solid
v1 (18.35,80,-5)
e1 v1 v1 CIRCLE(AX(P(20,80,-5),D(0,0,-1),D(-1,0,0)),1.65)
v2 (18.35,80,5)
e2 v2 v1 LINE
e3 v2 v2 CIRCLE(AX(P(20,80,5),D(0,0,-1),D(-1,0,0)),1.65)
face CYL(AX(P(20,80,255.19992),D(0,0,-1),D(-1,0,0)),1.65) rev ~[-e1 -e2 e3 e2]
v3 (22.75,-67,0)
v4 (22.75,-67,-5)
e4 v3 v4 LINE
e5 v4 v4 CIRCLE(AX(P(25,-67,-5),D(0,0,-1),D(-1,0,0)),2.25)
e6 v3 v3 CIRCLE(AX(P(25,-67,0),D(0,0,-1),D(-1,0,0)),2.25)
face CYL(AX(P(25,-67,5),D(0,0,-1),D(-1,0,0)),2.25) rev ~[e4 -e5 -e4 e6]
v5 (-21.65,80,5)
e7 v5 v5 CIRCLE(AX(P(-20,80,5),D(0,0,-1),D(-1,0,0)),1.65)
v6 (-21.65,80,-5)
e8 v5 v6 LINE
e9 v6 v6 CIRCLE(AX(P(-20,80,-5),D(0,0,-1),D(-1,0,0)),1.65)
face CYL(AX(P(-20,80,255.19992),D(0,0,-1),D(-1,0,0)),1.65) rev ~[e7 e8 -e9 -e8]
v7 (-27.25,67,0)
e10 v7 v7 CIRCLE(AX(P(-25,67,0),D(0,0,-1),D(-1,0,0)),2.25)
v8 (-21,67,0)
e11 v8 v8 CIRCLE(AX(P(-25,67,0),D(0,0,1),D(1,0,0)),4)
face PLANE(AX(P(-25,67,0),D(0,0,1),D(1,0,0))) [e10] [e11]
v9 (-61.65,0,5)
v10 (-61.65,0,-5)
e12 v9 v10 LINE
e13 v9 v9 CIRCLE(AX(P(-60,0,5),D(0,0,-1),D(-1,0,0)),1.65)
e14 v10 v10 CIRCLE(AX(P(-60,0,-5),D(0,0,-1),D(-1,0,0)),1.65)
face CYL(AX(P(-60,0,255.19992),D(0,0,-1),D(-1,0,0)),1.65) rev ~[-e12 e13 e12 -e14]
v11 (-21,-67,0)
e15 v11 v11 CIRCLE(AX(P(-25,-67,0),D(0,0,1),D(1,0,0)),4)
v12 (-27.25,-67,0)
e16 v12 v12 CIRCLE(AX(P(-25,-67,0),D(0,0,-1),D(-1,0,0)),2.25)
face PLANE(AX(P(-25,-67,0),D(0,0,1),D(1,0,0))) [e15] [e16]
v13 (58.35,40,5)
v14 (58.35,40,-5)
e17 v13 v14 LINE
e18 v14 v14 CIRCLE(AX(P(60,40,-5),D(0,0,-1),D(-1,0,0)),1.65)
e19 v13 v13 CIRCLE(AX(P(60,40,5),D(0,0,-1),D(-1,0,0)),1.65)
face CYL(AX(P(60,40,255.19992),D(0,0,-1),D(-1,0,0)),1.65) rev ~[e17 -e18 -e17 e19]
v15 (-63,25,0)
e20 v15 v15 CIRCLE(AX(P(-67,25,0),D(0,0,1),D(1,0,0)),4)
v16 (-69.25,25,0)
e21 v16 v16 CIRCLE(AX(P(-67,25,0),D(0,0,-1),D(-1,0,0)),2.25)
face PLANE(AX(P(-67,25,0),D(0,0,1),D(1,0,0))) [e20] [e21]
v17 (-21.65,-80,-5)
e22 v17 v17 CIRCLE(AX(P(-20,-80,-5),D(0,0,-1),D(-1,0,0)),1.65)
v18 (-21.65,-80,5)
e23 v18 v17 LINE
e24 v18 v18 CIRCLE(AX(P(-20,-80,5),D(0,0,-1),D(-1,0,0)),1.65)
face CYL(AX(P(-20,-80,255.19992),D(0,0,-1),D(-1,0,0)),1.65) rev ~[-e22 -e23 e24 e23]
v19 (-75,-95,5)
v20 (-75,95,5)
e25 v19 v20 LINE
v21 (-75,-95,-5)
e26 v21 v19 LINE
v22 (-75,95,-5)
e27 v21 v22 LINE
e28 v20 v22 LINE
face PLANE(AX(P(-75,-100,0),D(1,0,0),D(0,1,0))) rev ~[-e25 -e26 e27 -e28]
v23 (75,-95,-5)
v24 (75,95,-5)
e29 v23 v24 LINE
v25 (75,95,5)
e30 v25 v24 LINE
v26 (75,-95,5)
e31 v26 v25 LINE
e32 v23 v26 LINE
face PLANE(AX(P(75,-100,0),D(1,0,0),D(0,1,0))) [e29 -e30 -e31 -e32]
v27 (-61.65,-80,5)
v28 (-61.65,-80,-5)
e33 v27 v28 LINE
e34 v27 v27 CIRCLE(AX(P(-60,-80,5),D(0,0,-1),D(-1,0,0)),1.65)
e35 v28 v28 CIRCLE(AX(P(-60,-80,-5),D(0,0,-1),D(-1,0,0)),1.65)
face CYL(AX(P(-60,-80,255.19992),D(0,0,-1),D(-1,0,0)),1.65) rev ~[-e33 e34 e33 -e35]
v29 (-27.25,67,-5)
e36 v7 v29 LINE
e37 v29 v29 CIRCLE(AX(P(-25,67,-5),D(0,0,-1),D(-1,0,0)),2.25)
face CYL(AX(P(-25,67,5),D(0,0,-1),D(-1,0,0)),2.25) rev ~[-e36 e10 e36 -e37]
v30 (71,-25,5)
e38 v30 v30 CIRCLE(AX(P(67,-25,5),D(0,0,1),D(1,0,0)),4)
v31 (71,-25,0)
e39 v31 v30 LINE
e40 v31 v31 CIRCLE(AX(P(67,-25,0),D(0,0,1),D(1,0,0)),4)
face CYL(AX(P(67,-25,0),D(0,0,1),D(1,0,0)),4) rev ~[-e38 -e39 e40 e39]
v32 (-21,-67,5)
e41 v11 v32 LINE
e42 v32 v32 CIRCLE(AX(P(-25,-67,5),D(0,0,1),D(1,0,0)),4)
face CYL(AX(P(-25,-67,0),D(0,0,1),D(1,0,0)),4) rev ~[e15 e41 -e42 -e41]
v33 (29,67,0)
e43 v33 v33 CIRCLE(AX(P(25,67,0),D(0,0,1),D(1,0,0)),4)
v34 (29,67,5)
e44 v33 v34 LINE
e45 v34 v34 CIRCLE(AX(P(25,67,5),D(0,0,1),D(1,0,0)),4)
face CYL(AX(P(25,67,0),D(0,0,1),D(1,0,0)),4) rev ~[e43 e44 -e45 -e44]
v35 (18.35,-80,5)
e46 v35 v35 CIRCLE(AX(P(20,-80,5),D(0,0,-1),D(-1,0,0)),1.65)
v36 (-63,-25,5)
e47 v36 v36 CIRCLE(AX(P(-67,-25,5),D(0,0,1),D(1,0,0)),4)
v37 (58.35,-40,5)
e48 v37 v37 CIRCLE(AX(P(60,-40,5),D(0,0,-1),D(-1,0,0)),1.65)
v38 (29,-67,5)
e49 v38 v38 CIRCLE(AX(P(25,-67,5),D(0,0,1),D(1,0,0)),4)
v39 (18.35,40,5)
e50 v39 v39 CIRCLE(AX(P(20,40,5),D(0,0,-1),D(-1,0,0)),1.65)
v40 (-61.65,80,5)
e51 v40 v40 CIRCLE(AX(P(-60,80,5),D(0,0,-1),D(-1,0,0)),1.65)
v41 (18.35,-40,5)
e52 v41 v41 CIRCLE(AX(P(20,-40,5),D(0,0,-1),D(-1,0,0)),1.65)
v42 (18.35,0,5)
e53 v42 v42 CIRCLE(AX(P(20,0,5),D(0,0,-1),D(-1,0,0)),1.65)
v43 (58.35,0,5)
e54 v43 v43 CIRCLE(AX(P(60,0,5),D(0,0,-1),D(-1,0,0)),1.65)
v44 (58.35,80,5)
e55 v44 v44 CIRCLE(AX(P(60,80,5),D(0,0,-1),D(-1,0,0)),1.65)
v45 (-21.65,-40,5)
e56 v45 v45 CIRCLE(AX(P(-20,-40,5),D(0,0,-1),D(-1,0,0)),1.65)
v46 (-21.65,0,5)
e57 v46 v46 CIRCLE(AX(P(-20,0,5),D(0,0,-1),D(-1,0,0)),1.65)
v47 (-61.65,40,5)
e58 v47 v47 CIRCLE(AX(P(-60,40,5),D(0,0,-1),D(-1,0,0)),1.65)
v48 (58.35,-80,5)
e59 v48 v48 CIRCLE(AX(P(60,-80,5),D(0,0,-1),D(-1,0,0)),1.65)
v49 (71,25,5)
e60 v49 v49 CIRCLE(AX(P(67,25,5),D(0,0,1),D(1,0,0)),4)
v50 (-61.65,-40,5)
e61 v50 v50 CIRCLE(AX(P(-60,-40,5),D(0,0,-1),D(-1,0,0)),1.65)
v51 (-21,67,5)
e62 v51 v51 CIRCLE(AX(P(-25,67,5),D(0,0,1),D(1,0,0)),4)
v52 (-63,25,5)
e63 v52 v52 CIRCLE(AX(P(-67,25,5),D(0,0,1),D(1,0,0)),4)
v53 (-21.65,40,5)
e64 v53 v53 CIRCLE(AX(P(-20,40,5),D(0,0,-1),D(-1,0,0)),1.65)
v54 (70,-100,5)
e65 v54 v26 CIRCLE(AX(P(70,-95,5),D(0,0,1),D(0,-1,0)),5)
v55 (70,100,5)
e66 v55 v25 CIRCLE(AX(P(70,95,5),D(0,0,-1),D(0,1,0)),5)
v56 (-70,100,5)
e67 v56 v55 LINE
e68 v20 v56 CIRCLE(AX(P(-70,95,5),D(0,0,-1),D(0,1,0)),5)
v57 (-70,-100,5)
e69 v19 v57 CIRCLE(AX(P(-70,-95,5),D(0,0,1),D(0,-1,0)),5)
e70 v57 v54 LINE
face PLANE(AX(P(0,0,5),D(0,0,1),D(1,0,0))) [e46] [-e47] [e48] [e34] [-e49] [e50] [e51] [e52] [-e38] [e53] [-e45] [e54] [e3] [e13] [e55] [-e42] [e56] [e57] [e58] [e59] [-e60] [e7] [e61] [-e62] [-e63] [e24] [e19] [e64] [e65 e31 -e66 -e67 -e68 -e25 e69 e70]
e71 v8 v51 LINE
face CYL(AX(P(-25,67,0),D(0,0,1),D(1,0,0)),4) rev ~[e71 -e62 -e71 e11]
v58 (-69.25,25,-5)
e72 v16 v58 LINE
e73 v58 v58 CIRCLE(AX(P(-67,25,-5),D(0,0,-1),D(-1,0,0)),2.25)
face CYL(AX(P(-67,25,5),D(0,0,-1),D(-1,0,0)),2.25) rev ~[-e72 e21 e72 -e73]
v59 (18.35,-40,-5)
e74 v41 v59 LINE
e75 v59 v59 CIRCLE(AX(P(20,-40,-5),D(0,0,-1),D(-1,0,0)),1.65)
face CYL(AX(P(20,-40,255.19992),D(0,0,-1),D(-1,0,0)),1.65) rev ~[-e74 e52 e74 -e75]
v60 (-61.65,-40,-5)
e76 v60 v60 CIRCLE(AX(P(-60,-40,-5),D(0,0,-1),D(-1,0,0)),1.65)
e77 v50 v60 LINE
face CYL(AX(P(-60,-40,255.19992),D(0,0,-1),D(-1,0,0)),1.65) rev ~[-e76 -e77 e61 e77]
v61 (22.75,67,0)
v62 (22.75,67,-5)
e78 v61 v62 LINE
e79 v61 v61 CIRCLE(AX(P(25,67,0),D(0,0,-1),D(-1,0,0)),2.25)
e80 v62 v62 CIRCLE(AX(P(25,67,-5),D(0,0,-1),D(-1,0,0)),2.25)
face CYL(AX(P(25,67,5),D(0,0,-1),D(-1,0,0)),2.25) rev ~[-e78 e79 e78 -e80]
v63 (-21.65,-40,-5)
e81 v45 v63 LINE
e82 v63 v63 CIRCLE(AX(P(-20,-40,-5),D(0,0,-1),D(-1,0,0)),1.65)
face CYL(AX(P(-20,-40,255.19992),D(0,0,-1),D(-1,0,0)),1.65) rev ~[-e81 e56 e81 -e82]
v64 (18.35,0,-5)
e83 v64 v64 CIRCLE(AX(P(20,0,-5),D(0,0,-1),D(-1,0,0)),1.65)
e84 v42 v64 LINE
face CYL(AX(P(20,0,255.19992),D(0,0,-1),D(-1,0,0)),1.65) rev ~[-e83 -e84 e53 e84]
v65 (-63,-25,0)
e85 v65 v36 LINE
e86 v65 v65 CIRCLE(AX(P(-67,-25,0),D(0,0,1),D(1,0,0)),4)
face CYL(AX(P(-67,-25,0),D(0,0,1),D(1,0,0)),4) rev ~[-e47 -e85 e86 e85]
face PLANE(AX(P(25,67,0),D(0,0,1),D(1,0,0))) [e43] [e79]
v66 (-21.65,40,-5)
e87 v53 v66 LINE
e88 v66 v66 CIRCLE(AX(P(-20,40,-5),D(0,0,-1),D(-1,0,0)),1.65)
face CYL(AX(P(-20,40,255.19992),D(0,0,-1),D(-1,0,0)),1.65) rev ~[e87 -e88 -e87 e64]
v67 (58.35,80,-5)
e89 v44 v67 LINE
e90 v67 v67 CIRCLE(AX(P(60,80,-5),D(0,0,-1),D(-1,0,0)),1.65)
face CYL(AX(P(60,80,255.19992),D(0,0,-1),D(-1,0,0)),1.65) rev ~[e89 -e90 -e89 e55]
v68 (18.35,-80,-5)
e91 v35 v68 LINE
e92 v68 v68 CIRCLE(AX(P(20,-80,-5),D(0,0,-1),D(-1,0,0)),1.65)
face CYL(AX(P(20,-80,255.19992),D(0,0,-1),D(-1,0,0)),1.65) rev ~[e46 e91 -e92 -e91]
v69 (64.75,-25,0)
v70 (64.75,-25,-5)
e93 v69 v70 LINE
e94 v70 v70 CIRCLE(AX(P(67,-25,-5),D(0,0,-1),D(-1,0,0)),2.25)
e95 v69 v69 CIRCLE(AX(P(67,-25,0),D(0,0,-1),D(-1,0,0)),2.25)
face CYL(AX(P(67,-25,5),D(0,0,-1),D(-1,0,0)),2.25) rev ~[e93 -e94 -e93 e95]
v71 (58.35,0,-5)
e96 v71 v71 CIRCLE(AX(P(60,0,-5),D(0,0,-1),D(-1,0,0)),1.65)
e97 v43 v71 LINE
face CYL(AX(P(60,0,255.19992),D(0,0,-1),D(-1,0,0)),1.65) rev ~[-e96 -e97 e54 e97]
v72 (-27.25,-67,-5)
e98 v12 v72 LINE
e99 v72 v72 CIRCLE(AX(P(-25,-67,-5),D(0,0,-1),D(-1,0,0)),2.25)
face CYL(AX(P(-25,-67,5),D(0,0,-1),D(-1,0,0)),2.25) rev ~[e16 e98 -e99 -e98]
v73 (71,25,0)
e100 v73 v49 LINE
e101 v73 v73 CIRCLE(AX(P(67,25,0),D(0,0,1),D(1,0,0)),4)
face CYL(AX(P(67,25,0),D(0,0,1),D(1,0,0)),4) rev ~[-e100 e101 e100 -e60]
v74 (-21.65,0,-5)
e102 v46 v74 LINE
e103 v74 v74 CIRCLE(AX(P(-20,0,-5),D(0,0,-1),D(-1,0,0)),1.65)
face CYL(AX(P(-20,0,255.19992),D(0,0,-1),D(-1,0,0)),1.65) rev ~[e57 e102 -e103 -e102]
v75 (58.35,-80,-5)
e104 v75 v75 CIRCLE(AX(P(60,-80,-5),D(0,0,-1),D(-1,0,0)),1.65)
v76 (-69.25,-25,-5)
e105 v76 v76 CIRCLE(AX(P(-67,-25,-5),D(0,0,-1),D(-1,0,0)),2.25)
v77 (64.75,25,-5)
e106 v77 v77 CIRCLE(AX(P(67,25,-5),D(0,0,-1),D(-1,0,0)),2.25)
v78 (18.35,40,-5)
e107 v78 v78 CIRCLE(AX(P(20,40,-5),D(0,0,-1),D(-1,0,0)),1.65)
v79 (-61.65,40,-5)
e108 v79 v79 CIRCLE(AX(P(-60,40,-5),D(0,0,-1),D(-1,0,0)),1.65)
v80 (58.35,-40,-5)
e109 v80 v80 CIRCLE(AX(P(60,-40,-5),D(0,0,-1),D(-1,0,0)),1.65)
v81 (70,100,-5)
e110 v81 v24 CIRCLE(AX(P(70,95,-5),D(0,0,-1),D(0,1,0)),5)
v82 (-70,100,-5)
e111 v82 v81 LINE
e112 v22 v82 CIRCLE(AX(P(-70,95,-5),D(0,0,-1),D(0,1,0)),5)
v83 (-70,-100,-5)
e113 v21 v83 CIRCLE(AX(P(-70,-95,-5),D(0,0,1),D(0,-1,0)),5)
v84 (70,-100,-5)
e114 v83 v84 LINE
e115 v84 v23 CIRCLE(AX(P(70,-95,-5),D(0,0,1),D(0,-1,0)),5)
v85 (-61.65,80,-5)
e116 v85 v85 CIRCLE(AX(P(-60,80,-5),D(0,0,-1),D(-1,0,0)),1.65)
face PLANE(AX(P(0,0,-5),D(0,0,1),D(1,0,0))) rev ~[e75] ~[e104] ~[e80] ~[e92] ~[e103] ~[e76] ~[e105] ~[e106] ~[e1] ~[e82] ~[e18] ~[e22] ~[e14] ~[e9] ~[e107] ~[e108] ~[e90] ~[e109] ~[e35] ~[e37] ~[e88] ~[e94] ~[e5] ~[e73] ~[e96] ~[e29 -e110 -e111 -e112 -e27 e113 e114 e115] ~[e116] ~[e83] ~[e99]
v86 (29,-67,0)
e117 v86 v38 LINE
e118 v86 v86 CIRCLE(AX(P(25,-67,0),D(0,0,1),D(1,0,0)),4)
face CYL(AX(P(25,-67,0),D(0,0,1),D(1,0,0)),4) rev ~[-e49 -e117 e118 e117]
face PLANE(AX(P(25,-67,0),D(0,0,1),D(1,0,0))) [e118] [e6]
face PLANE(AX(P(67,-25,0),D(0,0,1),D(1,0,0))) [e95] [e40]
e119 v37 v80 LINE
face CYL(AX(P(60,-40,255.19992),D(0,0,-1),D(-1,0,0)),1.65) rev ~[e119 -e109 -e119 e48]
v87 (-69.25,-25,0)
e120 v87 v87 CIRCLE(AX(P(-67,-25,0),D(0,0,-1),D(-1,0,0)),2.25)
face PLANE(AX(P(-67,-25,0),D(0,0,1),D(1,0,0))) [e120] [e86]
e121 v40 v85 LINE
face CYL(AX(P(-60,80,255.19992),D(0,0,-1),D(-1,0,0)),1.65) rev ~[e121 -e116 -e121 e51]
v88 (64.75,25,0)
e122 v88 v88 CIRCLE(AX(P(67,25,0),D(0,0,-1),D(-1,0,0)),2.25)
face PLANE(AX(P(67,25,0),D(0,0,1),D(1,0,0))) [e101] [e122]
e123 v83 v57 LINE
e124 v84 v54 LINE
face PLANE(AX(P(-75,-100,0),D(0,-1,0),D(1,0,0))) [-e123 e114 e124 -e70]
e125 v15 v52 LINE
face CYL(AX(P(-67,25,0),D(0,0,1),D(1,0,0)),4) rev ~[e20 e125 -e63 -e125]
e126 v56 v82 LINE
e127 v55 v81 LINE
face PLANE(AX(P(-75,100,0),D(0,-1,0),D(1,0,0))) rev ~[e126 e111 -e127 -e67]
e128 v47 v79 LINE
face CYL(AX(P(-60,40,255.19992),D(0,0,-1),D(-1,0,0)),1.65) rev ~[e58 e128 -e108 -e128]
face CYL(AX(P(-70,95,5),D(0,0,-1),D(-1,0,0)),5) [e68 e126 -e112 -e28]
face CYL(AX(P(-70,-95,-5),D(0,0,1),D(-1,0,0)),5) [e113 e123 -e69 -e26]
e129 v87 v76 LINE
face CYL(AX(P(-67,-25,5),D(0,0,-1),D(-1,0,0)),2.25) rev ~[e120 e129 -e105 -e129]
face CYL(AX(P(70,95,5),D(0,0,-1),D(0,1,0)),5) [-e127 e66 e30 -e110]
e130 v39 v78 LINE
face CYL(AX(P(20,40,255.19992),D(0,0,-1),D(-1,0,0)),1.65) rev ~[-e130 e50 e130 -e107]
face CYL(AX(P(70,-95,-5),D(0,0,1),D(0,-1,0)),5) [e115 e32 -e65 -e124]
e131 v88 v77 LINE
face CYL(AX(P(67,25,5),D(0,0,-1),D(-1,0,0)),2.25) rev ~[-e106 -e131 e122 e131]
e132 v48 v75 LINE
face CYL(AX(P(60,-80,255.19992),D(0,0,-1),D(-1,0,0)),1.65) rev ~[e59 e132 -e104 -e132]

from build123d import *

# Parameters (mm, degrees)
SKETCH_1_W                  = 150
SKETCH_1_H                  = 200
SKETCH_1_R                  = 2
EXTRUDE_1_DEPTH             = 5
SKETCH_2_R                  = 4
CUT_EXTRUDE_1_DEPTH         = 4.5
HOLE_WIZARD_M4_1_D          = 3.3
HOLE_WIZARD_1_D             = 4.5
HOLE_WIZARD_1_CBORE_D       = 8
HOLE_WIZARD_1_CBORE_DEPTH   = 5
SKETCH_7_R                  = 4.920568007
SKETCH_7_R_2                = 5.393736445
SKETCH_7_R_3                = 5.34126294
SKETCH_7_R_4                = 5.362446972
EXTRUDE_2_DEPTH             = 10
FILLET_1_R                  = 5
HOLE_WIZARD_2_D             = 4.5
HOLE_WIZARD_2_CBORE_D       = 8
HOLE_WIZARD_2_CBORE_DEPTH   = 5
PATTERN_LINEAR_2_COUNT      = 4
PATTERN_LINEAR_2_PITCH      = 40
PATTERN_LINEAR_2_COUNT_DIR2 = 5
PATTERN_LINEAR_2_PITCH_DIR2 = 40


with BuildPart() as part:
    # 草图1 → 凸台-拉伸1 (new, symmetric)
    with BuildSketch(Plane.XY):
        Rectangle(SKETCH_1_W, SKETCH_1_H)
        with Locations((-67, 25)):
            Circle(SKETCH_1_R, mode=Mode.SUBTRACT)
        with Locations(Location((-67, -25, 0), (0, 0, 180))):
            Circle(SKETCH_1_R, mode=Mode.SUBTRACT)
        with Locations((67, -25)):
            Circle(SKETCH_1_R, mode=Mode.SUBTRACT)
        with Locations(Location((67, 25, 0), (0, 0, 180))):
            Circle(SKETCH_1_R, mode=Mode.SUBTRACT)
    extrude(amount=EXTRUDE_1_DEPTH, both=True)

    # 草图2 → 切除-拉伸1 (cut)
    with BuildSketch(Plane.XY.offset(5)):
        with Locations((67, 25)):
            Circle(SKETCH_2_R)
        with Locations((67, -25)):
            Circle(SKETCH_2_R)
        with Locations((-67, -25)):
            Circle(SKETCH_2_R)
        with Locations((-67, 25)):
            Circle(SKETCH_2_R)
    extrude(amount=-CUT_EXTRUDE_1_DEPTH, mode=Mode.SUBTRACT)

    # M4 螺纹孔1 (through all)
    with Locations(Plane.XY.offset(5)):
        with Locations((-60, 80)):
            hole_wizard_m4_1 = Hole(HOLE_WIZARD_M4_1_D / 2)

    # 打孔尺寸(%根据)开槽圆柱头螺钉的类型1 (through all)
    with Locations(Plane.XY.offset(5)):
        with Locations((-25, 67), (25, 67), (-25, -67), (25, -67)):
            CounterBoreHole(HOLE_WIZARD_1_D / 2, HOLE_WIZARD_1_CBORE_D / 2, HOLE_WIZARD_1_CBORE_DEPTH)

    # 草图7 → 凸台-拉伸2 (add)
    with BuildSketch(Plane.XY.offset(5)):
        with Locations((-67, 25)):
            Circle(SKETCH_7_R)
        with Locations((-67, -25)):
            Circle(SKETCH_7_R_2)
        with Locations((67, -25)):
            Circle(SKETCH_7_R_3)
        with Locations((67, 25)):
            Circle(SKETCH_7_R_4)
    extrude(amount=-EXTRUDE_2_DEPTH)

    # 圆角1
    fillet_1_edges = [part.edges().sort_by_distance(p)[0] for p in [
        (75, -100, 0),
        (-75, -100, 0),
        (-75, 100, 0),
        (75, 100, 0),
    ]]
    fillet(fillet_1_edges, radius=FILLET_1_R)

    # 打孔尺寸(%根据)开槽圆柱头螺钉的类型2 (through all)
    with Locations(Plane.XY.offset(5)):
        with Locations((-67, 25), (67, 25), (-67, -25), (67, -25)):
            CounterBoreHole(HOLE_WIZARD_2_D / 2, HOLE_WIZARD_2_CBORE_D / 2, HOLE_WIZARD_2_CBORE_DEPTH)

    # 阵列(线性)2: Hole Wizard M4 _1 4 × 5
    with Locations(*[(i * PATTERN_LINEAR_2_PITCH, -j * PATTERN_LINEAR_2_PITCH_DIR2, 0) for i in range(PATTERN_LINEAR_2_COUNT) for j in range(PATTERN_LINEAR_2_COUNT_DIR2) if (i, j) != (0, 0)]):
        add(hole_wizard_m4_1, mode=Mode.SUBTRACT)


solid = part.part
